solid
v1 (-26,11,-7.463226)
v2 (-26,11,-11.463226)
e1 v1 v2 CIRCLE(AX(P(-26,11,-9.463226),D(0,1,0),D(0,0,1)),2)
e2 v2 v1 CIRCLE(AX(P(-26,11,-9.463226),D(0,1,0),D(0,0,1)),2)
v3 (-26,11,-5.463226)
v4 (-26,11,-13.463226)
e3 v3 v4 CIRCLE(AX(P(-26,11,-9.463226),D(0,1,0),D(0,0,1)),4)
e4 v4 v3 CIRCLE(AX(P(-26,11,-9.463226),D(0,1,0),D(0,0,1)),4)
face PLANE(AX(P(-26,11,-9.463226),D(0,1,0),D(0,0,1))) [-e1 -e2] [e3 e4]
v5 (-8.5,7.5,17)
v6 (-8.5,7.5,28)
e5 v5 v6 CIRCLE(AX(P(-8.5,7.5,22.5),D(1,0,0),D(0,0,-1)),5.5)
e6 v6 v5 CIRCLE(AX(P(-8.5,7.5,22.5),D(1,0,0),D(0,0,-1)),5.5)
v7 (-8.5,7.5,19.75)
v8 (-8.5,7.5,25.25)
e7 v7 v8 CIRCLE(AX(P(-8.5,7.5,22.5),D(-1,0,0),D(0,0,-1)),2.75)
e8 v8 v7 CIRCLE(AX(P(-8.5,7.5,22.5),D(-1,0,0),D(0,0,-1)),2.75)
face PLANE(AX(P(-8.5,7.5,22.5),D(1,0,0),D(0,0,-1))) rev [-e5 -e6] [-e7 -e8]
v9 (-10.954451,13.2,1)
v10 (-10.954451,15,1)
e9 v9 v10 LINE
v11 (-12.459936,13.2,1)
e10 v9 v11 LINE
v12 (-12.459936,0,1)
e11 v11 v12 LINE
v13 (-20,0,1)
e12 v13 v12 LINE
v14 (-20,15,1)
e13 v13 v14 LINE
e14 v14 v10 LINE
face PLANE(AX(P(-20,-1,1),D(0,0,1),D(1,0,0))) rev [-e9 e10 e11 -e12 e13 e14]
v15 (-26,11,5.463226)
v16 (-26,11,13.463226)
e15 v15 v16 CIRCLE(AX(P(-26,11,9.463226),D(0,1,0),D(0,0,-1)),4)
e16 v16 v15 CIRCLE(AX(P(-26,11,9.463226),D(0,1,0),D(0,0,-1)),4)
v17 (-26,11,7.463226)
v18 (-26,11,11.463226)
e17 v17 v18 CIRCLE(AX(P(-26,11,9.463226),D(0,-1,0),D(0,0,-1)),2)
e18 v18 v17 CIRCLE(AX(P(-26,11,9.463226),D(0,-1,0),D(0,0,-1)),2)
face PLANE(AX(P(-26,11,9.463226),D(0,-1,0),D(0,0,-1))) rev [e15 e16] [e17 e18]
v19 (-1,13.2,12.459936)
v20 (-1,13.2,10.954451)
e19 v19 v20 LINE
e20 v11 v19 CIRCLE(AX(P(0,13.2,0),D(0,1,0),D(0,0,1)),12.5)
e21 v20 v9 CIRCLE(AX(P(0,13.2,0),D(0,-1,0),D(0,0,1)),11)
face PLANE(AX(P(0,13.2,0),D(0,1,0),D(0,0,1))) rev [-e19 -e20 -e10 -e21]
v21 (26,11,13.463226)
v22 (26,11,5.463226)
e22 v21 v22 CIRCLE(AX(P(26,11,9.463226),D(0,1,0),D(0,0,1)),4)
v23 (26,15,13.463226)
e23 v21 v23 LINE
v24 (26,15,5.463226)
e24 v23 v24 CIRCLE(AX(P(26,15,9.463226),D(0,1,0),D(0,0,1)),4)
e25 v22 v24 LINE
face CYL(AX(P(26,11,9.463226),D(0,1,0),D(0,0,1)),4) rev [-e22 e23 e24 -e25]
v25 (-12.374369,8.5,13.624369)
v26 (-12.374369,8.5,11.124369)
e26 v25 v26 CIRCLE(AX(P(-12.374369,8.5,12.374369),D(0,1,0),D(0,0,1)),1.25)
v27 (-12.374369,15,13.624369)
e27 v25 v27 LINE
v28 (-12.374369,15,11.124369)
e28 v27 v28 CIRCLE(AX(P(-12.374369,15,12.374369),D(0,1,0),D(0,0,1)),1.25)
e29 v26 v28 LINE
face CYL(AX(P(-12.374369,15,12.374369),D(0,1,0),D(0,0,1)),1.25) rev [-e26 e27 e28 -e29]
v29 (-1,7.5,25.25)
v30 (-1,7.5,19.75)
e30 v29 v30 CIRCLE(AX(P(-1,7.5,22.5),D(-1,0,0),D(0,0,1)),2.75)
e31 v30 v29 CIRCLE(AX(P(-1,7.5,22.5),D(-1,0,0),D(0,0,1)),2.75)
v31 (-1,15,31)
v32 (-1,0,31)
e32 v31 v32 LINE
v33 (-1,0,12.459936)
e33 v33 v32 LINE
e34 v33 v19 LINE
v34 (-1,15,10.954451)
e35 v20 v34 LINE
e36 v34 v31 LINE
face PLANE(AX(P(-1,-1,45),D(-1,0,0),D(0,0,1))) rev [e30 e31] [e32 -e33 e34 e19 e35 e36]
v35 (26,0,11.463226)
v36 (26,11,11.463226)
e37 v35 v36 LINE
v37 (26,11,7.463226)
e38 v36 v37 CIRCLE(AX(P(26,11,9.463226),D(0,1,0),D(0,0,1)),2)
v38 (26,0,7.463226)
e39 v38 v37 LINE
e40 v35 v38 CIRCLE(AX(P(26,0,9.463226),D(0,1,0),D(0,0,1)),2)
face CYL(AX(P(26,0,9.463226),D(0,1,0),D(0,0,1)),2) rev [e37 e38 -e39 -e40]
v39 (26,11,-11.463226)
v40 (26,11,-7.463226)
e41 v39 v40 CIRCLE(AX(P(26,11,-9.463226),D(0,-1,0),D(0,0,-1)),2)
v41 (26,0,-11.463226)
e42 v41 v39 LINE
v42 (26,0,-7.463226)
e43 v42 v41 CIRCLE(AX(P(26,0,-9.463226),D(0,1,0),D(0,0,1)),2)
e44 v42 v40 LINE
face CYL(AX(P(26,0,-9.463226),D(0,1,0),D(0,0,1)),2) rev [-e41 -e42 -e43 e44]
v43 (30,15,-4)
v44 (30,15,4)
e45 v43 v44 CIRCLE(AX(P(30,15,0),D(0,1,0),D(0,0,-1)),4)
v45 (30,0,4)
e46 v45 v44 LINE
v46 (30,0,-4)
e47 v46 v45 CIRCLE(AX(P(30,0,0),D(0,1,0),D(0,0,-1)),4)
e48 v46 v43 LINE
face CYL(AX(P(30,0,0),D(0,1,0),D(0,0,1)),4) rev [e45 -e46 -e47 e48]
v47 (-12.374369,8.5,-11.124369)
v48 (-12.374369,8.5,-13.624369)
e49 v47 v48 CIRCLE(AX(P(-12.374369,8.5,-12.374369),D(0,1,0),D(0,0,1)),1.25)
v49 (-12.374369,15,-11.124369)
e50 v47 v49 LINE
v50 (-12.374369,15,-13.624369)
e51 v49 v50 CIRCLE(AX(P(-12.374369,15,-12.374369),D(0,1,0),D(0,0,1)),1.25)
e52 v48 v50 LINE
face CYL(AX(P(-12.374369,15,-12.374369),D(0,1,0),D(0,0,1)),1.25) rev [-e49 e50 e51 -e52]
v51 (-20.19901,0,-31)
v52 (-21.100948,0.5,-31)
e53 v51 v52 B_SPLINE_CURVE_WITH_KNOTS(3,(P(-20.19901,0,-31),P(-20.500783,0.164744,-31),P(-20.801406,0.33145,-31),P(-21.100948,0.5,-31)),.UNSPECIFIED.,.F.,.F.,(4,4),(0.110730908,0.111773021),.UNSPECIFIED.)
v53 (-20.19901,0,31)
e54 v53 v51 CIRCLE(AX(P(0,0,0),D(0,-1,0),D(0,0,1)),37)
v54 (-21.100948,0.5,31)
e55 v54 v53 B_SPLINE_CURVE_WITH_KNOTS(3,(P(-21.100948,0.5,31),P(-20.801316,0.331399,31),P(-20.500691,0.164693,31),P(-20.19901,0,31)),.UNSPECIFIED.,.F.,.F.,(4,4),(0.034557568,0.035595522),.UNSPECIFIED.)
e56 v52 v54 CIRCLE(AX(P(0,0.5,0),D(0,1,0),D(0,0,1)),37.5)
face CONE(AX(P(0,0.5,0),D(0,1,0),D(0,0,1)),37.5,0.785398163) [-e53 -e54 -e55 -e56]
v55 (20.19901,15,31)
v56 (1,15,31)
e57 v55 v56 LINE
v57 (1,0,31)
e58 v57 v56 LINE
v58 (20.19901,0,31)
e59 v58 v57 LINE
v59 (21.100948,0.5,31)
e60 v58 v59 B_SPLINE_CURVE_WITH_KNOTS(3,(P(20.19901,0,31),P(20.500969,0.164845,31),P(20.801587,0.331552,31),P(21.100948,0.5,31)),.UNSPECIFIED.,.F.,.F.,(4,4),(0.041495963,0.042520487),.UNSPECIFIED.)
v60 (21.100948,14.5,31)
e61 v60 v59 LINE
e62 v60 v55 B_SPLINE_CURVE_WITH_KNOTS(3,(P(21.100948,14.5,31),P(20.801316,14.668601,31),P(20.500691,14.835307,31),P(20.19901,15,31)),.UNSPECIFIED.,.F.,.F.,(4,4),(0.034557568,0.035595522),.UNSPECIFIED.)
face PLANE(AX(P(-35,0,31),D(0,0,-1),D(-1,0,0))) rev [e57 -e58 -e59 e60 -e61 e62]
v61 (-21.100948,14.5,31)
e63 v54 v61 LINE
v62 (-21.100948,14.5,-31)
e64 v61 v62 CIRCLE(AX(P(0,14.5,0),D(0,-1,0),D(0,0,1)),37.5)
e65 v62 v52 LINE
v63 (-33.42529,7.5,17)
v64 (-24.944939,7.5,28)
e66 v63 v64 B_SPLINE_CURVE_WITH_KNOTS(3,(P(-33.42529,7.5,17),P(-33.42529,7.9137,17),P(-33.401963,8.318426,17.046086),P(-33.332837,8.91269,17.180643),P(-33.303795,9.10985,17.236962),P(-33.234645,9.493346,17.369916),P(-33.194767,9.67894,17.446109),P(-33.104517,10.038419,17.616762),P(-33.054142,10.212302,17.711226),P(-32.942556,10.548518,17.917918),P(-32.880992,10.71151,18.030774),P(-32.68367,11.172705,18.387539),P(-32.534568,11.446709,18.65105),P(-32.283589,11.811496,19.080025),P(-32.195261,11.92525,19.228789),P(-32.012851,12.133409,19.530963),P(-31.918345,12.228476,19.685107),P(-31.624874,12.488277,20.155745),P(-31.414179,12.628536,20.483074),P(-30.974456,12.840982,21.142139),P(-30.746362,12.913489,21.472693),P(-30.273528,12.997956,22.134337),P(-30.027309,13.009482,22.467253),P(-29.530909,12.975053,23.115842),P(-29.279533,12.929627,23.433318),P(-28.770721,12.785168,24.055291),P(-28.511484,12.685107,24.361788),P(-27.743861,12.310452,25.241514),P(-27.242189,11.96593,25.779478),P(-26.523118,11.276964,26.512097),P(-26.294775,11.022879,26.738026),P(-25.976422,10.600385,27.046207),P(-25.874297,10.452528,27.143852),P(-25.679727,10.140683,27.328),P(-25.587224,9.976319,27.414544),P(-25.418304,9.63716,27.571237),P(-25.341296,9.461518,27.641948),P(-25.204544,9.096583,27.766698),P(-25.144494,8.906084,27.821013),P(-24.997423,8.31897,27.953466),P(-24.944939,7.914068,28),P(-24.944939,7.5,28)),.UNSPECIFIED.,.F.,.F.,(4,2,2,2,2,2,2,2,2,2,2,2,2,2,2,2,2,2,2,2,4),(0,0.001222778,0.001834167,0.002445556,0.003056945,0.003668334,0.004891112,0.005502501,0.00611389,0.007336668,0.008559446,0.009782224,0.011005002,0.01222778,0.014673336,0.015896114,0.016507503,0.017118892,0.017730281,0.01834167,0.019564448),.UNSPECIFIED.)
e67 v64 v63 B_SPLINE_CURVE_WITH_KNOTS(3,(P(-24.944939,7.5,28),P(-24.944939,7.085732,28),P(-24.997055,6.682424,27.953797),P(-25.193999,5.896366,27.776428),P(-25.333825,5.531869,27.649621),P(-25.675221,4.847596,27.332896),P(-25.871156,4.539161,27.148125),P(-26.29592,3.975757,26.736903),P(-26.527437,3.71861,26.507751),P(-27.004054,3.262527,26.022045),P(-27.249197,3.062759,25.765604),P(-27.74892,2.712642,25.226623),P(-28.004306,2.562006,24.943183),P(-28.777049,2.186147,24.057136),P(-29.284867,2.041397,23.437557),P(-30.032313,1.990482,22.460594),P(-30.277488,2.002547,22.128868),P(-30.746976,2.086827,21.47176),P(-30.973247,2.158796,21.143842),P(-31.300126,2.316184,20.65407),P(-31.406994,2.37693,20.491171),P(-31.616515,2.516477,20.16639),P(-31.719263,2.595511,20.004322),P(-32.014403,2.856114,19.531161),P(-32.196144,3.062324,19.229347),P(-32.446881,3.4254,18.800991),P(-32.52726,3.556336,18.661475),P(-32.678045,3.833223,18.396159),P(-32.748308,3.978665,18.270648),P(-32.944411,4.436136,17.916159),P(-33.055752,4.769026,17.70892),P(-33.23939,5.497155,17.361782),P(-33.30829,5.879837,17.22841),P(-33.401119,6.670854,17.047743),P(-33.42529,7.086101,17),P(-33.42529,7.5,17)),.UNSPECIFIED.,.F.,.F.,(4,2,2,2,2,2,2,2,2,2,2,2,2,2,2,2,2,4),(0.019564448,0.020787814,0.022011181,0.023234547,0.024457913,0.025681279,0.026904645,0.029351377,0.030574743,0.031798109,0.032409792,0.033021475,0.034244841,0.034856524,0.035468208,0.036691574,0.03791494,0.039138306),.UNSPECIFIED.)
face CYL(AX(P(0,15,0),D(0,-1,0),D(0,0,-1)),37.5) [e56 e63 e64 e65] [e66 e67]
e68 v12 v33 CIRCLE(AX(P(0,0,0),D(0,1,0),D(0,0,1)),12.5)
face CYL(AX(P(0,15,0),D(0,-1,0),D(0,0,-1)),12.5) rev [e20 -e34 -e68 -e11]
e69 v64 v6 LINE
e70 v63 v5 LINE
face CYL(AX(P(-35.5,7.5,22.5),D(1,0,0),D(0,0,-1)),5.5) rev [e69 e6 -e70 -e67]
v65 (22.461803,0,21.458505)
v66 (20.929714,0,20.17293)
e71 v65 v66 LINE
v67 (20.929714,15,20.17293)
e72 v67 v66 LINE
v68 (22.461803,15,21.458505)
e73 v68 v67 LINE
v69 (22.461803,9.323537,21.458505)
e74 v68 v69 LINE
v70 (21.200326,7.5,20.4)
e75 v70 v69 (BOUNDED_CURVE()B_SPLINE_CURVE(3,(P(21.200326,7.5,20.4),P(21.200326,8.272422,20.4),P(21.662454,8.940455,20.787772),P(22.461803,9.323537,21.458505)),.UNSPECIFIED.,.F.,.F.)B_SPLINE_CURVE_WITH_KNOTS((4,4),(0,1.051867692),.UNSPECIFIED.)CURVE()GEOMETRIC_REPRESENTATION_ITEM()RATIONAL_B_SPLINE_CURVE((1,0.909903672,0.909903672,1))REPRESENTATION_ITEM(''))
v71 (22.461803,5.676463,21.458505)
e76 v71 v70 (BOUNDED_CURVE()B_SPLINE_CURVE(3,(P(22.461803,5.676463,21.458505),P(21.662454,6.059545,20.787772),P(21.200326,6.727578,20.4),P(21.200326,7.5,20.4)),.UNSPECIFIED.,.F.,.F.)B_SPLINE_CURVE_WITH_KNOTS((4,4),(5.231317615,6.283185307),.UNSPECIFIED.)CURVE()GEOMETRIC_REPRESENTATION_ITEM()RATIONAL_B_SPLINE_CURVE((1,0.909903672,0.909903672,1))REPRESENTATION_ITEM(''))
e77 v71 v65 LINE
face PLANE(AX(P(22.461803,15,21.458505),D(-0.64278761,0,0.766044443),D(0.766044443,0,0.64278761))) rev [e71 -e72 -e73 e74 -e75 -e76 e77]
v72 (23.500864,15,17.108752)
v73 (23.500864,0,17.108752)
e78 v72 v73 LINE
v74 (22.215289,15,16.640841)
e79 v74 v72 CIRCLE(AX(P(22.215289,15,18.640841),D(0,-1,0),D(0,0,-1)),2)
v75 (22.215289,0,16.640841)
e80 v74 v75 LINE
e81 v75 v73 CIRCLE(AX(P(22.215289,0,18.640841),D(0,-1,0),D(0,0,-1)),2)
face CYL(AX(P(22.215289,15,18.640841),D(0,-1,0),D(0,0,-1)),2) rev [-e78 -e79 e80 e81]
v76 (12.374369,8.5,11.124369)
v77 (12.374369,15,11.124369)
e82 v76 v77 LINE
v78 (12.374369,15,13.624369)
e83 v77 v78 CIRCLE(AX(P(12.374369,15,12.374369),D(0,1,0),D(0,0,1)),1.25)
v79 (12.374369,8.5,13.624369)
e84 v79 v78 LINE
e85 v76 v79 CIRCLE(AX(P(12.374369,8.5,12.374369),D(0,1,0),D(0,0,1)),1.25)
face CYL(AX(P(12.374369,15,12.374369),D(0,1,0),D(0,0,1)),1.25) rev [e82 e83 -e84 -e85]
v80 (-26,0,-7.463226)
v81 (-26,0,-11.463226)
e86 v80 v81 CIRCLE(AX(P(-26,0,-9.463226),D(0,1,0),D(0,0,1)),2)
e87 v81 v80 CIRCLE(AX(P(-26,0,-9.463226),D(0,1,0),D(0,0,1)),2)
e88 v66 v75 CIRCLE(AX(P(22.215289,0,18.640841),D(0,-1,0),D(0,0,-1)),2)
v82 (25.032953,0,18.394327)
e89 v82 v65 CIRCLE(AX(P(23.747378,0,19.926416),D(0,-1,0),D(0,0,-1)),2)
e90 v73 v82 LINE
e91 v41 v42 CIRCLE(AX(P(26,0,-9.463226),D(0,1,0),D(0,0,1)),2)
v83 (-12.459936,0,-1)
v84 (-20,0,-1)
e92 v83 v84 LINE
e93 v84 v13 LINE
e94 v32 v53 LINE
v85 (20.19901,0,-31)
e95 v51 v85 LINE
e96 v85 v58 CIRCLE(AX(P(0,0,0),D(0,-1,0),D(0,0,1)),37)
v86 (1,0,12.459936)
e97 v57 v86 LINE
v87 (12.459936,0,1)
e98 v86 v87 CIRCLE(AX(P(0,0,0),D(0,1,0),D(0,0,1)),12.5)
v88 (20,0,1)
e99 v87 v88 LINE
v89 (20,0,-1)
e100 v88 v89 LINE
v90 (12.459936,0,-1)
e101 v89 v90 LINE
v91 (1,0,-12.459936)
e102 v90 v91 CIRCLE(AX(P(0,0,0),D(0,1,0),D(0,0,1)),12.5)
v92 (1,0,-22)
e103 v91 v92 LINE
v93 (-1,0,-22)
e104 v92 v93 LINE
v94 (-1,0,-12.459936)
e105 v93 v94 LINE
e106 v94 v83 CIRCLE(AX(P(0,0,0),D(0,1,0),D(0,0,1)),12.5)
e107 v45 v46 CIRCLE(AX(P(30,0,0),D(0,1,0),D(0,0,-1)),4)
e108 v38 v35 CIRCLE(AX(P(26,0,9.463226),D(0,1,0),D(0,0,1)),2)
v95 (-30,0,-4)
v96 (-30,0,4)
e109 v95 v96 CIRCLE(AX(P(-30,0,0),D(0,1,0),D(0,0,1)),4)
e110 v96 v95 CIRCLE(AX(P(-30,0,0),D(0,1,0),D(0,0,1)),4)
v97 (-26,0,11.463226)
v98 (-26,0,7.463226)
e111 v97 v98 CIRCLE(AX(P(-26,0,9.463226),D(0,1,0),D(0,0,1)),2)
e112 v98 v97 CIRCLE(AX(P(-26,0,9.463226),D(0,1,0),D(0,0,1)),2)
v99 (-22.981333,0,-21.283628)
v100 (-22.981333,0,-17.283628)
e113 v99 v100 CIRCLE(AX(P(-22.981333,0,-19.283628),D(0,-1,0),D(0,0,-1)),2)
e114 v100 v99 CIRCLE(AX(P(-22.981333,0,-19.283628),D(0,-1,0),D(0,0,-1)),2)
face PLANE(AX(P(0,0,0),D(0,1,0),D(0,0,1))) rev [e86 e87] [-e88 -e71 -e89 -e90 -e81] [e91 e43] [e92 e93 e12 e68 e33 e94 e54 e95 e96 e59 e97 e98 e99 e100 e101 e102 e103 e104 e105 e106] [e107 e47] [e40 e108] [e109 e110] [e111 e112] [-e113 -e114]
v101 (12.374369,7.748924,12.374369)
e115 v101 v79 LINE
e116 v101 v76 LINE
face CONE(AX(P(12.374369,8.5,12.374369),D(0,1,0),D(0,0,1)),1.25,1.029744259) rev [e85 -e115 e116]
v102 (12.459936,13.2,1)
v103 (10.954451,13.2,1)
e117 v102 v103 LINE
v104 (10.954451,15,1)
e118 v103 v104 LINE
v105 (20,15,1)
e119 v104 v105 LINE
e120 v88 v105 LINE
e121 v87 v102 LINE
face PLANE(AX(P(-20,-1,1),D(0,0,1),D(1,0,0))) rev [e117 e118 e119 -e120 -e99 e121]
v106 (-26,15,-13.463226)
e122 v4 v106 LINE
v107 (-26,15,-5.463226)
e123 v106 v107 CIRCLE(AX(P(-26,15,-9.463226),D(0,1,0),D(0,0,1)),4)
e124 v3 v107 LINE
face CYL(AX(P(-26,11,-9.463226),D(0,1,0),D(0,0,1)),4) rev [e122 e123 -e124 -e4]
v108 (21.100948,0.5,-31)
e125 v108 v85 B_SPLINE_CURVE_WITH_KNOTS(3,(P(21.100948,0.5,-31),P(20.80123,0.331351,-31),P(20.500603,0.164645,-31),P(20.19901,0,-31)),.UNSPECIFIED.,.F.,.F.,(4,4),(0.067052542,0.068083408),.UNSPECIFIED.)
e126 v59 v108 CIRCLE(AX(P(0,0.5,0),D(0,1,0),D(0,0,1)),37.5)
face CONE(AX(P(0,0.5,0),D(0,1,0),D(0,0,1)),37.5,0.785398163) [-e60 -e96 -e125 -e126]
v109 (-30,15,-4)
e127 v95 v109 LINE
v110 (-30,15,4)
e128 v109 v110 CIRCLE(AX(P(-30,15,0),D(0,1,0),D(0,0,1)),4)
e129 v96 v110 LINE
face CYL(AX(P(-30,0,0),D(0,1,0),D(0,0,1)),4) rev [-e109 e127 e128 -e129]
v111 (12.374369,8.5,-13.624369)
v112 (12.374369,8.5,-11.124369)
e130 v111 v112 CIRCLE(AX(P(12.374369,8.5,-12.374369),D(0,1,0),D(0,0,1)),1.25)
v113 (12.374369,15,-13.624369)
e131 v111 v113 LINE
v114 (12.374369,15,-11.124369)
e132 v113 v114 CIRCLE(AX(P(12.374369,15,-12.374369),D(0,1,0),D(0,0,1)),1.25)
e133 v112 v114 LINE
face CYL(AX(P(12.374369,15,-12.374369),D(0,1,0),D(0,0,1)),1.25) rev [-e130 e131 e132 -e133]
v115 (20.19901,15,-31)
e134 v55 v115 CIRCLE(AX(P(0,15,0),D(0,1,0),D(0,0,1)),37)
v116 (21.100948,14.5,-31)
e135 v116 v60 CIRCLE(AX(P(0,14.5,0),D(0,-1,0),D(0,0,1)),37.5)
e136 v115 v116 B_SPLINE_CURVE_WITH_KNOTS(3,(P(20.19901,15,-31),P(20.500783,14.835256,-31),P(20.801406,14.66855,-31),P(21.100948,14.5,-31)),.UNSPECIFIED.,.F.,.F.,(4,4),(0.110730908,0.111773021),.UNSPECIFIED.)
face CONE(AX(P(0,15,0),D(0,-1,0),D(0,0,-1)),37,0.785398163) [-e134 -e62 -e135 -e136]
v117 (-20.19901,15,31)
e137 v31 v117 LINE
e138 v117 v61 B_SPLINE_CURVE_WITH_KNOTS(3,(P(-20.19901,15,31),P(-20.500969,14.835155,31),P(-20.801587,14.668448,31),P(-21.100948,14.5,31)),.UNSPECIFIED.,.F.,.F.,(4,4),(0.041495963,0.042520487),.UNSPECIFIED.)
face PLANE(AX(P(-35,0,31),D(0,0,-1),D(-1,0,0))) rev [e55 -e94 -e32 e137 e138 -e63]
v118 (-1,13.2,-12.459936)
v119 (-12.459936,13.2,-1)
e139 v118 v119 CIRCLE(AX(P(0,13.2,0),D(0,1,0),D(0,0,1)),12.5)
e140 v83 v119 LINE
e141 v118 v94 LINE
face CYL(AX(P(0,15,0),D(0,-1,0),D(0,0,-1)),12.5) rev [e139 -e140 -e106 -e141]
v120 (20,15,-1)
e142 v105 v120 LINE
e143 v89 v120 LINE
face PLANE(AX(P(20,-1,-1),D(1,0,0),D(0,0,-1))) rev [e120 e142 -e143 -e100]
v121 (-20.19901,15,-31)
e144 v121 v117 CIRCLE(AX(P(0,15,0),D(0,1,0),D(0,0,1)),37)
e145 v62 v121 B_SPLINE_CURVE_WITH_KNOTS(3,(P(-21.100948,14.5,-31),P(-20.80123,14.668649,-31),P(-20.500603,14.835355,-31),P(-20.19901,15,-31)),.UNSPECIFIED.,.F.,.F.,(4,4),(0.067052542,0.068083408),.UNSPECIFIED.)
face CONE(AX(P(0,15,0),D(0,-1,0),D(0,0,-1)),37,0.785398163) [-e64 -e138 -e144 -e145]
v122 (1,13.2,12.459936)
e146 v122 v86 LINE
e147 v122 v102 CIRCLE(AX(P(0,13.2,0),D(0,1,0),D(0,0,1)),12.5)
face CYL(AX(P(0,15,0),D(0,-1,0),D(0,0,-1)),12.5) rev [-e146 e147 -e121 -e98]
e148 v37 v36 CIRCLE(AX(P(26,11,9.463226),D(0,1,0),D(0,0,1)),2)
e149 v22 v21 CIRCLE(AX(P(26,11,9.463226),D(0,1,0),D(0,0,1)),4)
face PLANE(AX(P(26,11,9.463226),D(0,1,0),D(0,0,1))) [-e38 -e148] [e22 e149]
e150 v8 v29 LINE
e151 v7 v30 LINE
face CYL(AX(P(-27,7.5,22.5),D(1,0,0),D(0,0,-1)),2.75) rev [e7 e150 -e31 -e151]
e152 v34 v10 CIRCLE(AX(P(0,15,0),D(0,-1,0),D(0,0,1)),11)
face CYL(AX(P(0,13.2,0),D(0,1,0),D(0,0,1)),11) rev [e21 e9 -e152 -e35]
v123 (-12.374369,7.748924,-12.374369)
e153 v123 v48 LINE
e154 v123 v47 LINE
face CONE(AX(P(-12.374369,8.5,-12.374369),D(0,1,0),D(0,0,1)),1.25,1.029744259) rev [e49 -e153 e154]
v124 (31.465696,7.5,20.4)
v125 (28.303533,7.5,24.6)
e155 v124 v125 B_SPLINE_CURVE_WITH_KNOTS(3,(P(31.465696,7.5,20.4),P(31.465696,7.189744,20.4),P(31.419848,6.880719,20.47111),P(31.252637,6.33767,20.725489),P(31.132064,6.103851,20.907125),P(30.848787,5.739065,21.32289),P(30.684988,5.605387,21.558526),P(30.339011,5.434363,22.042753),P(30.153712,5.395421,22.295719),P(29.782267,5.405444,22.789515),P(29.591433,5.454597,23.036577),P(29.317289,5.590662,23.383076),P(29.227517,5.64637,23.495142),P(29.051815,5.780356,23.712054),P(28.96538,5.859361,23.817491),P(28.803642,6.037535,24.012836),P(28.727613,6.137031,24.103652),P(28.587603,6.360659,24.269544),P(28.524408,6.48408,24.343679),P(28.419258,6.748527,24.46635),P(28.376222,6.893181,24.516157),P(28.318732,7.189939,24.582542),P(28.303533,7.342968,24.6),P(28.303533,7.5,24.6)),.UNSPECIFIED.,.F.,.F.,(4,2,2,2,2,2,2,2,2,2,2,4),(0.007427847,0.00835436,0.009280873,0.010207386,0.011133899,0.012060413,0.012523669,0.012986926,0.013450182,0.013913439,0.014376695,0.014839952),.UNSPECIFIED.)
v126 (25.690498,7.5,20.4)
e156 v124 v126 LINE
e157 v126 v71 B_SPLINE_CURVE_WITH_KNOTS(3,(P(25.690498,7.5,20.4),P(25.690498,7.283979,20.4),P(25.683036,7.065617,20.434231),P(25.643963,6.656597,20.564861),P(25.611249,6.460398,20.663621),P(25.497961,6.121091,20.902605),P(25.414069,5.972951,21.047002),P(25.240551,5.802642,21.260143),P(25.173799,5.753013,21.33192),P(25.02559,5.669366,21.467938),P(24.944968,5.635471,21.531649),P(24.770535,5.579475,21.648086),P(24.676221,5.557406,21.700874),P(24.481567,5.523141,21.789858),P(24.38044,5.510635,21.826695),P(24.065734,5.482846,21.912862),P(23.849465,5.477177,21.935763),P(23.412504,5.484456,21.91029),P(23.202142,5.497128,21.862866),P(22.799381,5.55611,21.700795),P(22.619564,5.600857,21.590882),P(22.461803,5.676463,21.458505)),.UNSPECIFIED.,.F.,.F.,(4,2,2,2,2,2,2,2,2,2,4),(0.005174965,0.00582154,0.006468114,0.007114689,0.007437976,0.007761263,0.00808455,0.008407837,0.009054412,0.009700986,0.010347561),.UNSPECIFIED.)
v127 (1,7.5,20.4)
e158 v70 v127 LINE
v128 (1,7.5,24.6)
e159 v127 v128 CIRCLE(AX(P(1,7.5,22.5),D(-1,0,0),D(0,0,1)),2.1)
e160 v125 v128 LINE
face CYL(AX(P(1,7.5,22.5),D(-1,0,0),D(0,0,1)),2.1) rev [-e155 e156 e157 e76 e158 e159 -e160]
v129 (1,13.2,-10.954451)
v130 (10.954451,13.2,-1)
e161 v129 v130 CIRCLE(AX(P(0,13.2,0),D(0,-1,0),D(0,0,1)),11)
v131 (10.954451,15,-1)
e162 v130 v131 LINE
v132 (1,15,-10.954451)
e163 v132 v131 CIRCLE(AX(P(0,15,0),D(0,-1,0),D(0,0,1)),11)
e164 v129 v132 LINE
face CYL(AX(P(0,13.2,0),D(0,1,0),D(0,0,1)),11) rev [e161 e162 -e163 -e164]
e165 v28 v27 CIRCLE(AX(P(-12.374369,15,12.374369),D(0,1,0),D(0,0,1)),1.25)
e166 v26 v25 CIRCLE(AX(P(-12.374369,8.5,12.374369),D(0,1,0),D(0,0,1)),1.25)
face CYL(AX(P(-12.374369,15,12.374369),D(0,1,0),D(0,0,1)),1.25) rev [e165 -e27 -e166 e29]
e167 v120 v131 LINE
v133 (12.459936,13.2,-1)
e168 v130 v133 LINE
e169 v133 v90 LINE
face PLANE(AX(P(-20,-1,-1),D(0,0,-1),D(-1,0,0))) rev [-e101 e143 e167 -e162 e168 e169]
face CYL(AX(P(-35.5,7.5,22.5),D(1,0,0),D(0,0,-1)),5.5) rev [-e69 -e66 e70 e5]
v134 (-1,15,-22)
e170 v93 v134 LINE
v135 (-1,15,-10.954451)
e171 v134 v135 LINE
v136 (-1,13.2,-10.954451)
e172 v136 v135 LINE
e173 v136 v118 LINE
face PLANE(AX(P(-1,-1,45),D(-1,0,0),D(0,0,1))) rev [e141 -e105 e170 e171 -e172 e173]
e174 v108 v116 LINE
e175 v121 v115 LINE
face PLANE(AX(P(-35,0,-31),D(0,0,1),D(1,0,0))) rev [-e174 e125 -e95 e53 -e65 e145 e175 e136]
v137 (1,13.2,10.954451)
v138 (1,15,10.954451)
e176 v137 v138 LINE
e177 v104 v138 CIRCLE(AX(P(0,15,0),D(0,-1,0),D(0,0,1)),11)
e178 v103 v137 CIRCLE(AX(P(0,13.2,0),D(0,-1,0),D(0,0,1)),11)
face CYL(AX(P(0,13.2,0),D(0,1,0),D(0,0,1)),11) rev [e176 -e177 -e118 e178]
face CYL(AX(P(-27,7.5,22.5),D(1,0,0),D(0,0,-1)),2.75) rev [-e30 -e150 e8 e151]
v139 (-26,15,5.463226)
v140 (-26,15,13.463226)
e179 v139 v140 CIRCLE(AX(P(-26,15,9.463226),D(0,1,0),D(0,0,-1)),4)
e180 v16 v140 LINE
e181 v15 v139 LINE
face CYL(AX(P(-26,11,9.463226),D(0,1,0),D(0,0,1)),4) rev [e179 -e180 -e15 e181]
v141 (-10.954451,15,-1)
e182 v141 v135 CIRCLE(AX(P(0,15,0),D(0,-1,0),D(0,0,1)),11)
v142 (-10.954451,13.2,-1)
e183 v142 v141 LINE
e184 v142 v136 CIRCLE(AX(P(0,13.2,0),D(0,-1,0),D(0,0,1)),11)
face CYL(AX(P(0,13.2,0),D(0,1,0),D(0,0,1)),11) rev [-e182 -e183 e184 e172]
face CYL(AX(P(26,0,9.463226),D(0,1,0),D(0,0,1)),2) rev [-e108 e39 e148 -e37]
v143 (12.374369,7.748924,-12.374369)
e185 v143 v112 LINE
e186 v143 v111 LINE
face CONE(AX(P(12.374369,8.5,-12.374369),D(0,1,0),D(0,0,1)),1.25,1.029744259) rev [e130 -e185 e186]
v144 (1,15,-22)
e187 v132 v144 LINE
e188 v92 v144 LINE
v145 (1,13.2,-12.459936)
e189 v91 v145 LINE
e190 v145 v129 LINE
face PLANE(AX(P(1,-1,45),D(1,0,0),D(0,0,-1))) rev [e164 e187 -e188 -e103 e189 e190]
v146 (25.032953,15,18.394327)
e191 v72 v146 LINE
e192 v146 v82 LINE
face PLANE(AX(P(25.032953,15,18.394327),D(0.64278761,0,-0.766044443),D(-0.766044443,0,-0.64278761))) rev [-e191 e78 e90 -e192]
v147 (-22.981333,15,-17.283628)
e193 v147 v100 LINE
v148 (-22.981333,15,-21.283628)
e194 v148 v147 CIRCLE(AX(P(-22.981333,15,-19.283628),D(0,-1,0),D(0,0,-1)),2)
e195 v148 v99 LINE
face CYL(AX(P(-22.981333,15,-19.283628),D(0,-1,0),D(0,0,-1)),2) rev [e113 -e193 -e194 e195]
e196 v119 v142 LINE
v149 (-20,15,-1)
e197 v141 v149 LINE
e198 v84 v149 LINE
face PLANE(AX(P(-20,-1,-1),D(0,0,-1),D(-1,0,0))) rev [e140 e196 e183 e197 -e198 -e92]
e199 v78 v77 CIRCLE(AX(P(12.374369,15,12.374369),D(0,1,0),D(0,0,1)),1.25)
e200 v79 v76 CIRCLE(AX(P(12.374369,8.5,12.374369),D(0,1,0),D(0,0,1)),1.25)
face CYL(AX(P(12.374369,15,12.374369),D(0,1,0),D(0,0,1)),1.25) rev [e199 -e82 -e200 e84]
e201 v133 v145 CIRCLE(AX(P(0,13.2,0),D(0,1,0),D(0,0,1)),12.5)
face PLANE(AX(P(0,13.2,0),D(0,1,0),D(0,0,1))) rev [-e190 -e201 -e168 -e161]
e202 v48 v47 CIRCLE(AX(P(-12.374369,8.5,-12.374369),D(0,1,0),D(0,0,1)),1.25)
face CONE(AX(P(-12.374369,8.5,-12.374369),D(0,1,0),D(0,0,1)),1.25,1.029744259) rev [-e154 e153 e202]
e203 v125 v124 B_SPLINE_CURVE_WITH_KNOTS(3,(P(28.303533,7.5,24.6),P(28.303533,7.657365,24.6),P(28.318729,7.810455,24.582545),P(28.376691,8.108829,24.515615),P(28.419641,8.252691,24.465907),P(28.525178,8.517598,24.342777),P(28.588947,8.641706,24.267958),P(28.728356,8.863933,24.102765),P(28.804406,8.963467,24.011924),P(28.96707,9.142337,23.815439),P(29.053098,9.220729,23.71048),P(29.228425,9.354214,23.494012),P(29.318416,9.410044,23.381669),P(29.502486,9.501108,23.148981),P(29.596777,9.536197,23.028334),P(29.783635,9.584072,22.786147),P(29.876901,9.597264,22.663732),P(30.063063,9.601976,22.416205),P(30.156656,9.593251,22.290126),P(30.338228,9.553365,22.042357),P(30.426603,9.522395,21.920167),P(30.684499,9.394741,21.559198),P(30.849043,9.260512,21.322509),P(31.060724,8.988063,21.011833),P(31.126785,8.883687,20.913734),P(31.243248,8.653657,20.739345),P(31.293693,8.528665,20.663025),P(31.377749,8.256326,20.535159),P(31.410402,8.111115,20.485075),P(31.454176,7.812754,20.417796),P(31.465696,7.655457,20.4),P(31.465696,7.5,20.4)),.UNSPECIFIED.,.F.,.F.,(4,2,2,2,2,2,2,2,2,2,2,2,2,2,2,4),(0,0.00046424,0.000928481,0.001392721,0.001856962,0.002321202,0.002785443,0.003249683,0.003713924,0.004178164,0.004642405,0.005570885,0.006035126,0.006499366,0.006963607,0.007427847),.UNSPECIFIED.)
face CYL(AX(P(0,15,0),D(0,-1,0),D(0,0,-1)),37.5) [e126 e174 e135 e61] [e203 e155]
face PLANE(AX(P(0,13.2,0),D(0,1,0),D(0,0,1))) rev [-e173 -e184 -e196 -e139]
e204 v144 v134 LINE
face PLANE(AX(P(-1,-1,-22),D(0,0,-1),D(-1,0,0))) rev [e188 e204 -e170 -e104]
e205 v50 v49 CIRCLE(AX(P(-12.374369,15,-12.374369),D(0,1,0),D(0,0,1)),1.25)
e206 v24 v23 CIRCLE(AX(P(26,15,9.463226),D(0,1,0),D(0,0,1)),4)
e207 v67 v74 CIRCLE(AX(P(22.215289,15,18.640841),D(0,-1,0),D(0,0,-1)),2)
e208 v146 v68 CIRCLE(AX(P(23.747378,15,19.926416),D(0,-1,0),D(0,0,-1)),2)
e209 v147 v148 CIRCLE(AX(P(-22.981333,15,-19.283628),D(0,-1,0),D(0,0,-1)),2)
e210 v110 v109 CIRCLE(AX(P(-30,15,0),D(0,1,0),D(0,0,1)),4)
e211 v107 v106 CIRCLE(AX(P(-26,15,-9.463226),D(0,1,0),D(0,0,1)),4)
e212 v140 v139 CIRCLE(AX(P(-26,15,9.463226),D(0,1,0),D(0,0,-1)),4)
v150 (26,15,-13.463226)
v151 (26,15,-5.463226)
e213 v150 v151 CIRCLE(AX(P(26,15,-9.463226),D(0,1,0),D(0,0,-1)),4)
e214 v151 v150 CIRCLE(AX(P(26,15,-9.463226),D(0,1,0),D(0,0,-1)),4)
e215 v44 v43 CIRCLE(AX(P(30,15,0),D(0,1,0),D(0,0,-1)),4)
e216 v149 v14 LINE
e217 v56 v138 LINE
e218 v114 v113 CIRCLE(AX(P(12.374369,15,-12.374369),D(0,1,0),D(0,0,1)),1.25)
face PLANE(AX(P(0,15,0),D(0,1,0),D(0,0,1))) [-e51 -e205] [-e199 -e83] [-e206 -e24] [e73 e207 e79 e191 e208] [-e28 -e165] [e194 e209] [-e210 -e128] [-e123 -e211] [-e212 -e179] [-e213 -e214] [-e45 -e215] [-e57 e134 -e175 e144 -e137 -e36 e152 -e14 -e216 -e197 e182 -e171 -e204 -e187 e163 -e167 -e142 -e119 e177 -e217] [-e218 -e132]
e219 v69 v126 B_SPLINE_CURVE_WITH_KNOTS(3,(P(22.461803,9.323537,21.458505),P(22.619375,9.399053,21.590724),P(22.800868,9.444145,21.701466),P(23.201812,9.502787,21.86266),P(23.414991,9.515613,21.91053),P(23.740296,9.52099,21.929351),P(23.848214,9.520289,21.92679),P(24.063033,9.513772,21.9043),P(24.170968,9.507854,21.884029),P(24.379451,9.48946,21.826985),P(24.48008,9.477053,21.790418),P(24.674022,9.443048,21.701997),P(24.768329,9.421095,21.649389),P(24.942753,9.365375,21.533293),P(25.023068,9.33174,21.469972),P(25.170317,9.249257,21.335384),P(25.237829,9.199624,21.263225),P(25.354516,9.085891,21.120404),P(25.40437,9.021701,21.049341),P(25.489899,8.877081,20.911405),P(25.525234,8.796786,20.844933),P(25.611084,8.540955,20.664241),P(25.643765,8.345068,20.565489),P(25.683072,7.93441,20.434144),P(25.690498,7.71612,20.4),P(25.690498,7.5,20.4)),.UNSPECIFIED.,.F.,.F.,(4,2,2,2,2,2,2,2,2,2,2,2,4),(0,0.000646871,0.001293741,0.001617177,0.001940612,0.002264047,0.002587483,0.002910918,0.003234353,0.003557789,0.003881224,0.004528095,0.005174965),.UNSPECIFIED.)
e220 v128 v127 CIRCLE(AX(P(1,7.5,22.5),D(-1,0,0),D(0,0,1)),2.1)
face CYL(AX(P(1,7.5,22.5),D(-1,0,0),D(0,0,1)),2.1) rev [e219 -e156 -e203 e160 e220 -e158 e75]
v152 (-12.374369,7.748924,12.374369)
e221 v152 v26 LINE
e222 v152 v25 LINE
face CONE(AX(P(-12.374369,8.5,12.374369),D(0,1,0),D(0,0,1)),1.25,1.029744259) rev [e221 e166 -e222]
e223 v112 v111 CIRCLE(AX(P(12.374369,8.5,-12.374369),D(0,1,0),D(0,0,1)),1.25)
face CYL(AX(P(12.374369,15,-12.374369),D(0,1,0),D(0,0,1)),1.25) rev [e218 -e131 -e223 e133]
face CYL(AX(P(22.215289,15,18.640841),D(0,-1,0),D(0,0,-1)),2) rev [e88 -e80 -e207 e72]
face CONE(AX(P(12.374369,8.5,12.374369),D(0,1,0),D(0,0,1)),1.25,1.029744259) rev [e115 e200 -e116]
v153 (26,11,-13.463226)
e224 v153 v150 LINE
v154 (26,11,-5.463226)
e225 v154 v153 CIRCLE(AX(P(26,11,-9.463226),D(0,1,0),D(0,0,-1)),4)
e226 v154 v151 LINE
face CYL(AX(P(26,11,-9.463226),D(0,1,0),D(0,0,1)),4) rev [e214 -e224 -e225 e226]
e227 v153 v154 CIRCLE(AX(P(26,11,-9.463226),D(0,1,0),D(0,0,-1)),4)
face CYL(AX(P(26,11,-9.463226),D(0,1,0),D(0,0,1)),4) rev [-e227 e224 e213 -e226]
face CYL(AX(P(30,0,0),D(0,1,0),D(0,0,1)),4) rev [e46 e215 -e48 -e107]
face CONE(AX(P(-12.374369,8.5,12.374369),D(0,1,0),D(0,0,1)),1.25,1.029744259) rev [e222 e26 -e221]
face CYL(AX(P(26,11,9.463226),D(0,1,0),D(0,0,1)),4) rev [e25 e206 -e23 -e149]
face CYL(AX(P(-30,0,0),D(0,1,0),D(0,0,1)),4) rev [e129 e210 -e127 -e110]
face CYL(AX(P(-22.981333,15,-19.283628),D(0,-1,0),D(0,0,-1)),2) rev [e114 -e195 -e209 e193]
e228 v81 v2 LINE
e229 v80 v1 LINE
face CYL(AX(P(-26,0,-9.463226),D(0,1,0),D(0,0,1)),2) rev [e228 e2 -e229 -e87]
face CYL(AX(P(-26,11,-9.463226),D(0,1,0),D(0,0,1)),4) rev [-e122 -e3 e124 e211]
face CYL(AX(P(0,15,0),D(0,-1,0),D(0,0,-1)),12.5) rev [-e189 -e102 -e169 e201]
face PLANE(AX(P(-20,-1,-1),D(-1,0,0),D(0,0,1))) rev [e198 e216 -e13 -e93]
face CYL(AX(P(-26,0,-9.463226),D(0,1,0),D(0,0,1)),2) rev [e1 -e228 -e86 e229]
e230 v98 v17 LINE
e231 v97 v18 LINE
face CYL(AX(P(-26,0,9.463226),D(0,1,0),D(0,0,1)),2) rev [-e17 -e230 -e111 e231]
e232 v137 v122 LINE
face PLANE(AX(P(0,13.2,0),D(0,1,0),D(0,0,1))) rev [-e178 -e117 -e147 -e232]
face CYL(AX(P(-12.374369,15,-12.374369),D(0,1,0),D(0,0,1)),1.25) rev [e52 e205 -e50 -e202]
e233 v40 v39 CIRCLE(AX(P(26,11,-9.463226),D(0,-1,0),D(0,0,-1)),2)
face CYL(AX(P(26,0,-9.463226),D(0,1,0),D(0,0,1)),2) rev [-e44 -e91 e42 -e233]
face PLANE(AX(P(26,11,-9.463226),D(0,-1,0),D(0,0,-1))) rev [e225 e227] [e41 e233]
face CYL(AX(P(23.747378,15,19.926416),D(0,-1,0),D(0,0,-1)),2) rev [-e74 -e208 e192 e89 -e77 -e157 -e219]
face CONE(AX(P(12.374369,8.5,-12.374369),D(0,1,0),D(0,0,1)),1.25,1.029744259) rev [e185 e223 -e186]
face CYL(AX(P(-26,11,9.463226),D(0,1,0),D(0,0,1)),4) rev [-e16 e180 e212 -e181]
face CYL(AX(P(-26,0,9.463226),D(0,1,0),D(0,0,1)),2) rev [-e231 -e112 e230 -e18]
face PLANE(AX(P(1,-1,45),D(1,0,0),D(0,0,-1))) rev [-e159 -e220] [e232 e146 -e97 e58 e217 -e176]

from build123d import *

# Parameters (mm, degrees)
SKETCH1_R           = 37.5
SKETCH1_R_2         = 12.5
BOSS_EXTRUDE1_DEPTH = 15
SKETCH2_R           = 4
CUT_EXTRUDE1_DEPTH  = 4
SKETCH3_R           = 2
CUT_EXTRUDE2_DEPTH  = 56.113519213
SKETCH4_W           = 40
SKETCH4_H           = 2
CUT_EXTRUDE3_DEPTH  = 16
SKETCH5_W           = 2
SKETCH5_H           = 67
CUT_EXTRUDE4_DEPTH  = 16
CHAMFER1_SIZE       = 0.5
SKETCH6_R           = 2.75
CUT_EXTRUDE5_DEPTH  = 27
SKETCH7_R           = 5.5
CUT_EXTRUDE6_DEPTH  = 27
SKETCH8_R           = 0.542778956
CUT_EXTRUDE7_DEPTH  = 27
M5_TAPPED_HOLE1_D   = 4.2
SKETCH10_R          = 4
CUT_EXTRUDE8_DEPTH  = 56.113519349
SKETCH11_W          = 70
SKETCH11_H          = 13
CUT_EXTRUDE9_DEPTH  = 56.113519349
SKETCH16_R          = 2
CUT_EXTRUDE11_DEPTH = 51.914143553
BOSS_EXTRUDE2_START = -1.8
BOSS_EXTRUDE2_DEPTH = 1.8
SKETCH19_R          = 1
CUT_EXTRUDE12_DEPTH = 5
CIRPATTERN2_COUNT   = 4


with BuildPart() as part:
    # Sketch1 → Boss-Extrude1 (new body)
    with BuildSketch(Plane(origin=(0, 0, 0), x_dir=(1, 0, 0), z_dir=(0, 1, 0))):
        with Locations(Location((0, 0, 0), (0, 0, 270))):
            Circle(SKETCH1_R)
        with Locations(Location((0, 0, 0), (0, 0, 270))):
            Circle(SKETCH1_R_2, mode=Mode.SUBTRACT)
    extrude(amount=BOSS_EXTRUDE1_DEPTH)

    # Sketch2 → Cut-Extrude1 (cut)
    with BuildSketch(Plane(origin=(0, 15, 0), x_dir=(1, 0, 0), z_dir=(0, 1, 0))):
        with Locations(Location((26, -9.463226091, 0), (0, 0, 270))):
            Circle(SKETCH2_R)
        with Locations(Location((-26, 9.463226091, 0), (0, 0, 270))):
            Circle(SKETCH2_R)
        with Locations(Location((-26, -9.463226091, 0), (0, 0, 90))):
            Circle(SKETCH2_R)
        with Locations(Location((26, 9.463226091, 0), (0, 0, 90))):
            Circle(SKETCH2_R)
    extrude(amount=-CUT_EXTRUDE1_DEPTH, mode=Mode.SUBTRACT)

    # Sketch3 → Cut-Extrude2 (cut, through all)
    with BuildSketch(Plane(origin=(0, 15, 0), x_dir=(1, 0, 0), z_dir=(0, 1, 0))):
        with Locations(Location((-26, 9.463226091, 0), (0, 0, 270))):
            Circle(SKETCH3_R)
        with Locations(Location((-26, -9.463226091, 0), (0, 0, 270))):
            Circle(SKETCH3_R)
        with Locations(Location((26, 9.463226091, 0), (0, 0, 270))):
            Circle(SKETCH3_R)
        with Locations(Location((26, -9.463226091, 0), (0, 0, 270))):
            Circle(SKETCH3_R)
    extrude(amount=-CUT_EXTRUDE2_DEPTH, mode=Mode.SUBTRACT)

    # Sketch4 → Cut-Extrude3 (cut)
    with BuildSketch(Plane(origin=(0, 15, 0), x_dir=(1, 0, 0), z_dir=(0, 1, 0))):
        Rectangle(SKETCH4_W, SKETCH4_H)
    extrude(amount=-CUT_EXTRUDE3_DEPTH, mode=Mode.SUBTRACT)

    # Sketch5 → Cut-Extrude4 (cut)
    with BuildSketch(Plane(origin=(0, 15, 0), x_dir=(1, 0, 0), z_dir=(0, 1, 0))):
        with Locations((0, -11.5)):
            Rectangle(SKETCH5_W, SKETCH5_H)
    extrude(amount=-CUT_EXTRUDE4_DEPTH, mode=Mode.SUBTRACT)

    # Chamfer1
    chamfer1_edges = [part.edges().sort_by_distance(p)[0] for p in [
        (0, 0, -37.5),
        (0, 15, -37.5),
    ]]
    chamfer(chamfer1_edges, length=CHAMFER1_SIZE)

    # Sketch6 → Cut-Extrude5 (cut)
    with BuildSketch(Plane(origin=(0, 0, 0), x_dir=(0, 0, -1), z_dir=(1, 0, 0))):
        with Locations((-22.5, 7.5)):
            Circle(SKETCH6_R)
    extrude(amount=-CUT_EXTRUDE5_DEPTH, mode=Mode.SUBTRACT)

    # Sketch7 → Cut-Extrude6 (cut)
    with BuildSketch(Plane(origin=(-8.5, 0, 0), x_dir=(0, 0, -1), z_dir=(1, 0, 0))):
        with Locations((-22.5, 7.5)):
            Circle(SKETCH7_R)
    extrude(amount=-CUT_EXTRUDE6_DEPTH, mode=Mode.SUBTRACT)

    # Sketch8 → Cut-Extrude7 (cut)
    with BuildSketch(Plane.ZY.offset(-1)):
        with Locations((22.5, 7.5)):
            Circle(SKETCH8_R)
    extrude(amount=-CUT_EXTRUDE7_DEPTH, mode=Mode.SUBTRACT)

    # M5 Tapped Hole1 (through all)
    with Locations(Plane(origin=(1, 7.5, 22.5), x_dir=(0, 0, -1), z_dir=(-1, 0, 0))):
        with Locations((0, 0)):
            Hole(M5_TAPPED_HOLE1_D / 2)

    # Sketch10 → Cut-Extrude8 (cut, through all)
    with BuildSketch(Plane(origin=(0, 15, 0), x_dir=(1, 0, 0), z_dir=(0, 1, 0))):
        with Locations(Location((-30, 0, 0), (0, 0, 270))):
            Circle(SKETCH10_R)
        with Locations(Location((30, 0, 0), (0, 0, 90))):
            Circle(SKETCH10_R)
    extrude(amount=-CUT_EXTRUDE8_DEPTH, mode=Mode.SUBTRACT)

    # Sketch11 → Cut-Extrude9 (cut, through all)
    with BuildSketch(Plane(origin=(0, 15, 0), x_dir=(1, 0, 0), z_dir=(0, 1, 0))):
        with Locations((0, -37.5)):
            Rectangle(SKETCH11_W, SKETCH11_H)
        with Locations((0, 37.5)):
            Rectangle(SKETCH11_W, SKETCH11_H)
    extrude(amount=-CUT_EXTRUDE9_DEPTH, mode=Mode.SUBTRACT)

    # Sketch16 → Cut-Extrude11 (cut, through all)
    with BuildSketch(Plane.XZ):
        with Locations(Location((-22.981333294, -19.283628291, 0), (0, 0, 270))):
            Circle(SKETCH16_R)
        with BuildLine():
            Line((25.032952956, 18.394327014), (23.50086407, 17.108751795))
            ThreePointArc((23.50086407, 17.108751795), (20.683199964, 17.355265462), (20.929713631, 20.172929567))
            Line((20.929713631, 20.172929567), (22.461802517, 21.458504787))
            ThreePointArc((22.461802517, 21.458504787), (25.279466623, 21.21199112), (25.032952956, 18.394327014))
        make_face()
    extrude(amount=-CUT_EXTRUDE11_DEPTH, mode=Mode.SUBTRACT)

    # Sketch17 → Boss-Extrude2 (add)
    with BuildSketch(Plane(origin=(0, 15, 0), x_dir=(1, 0, 0), z_dir=(0, 1, 0)).offset(BOSS_EXTRUDE2_START)):
        with BuildLine():
            Line((1, 12.459935794), (1, 10.95445115))
            ThreePointArc((1, 10.95445115), (7.778174593, 7.778174593), (10.95445115, 1))
            Line((10.95445115, 1), (12.459935794, 1))
            ThreePointArc((12.459935794, 1), (8.838834765, 8.838834765), (1, 12.459935794))
        make_face()
        with BuildLine():
            Line((-1, 12.459935794), (-1, 10.95445115))
            ThreePointArc((-1, 10.95445115), (-7.778174593, 7.778174593), (-10.95445115, 1))
            Line((-10.95445115, 1), (-12.459935794, 1))
            ThreePointArc((-12.459935794, 1), (-8.838834765, 8.838834765), (-1, 12.459935794))
        make_face()
        with BuildLine():
            Line((12.459935794, -1), (10.95445115, -1))
            ThreePointArc((10.95445115, -1), (7.778174593, -7.778174593), (1, -10.95445115))
            Line((1, -10.95445115), (1, -12.459935794))
            ThreePointArc((1, -12.459935794), (8.838834765, -8.838834765), (12.459935794, -1))
        make_face()
        with BuildLine():
            Line((-12.459935794, -1), (-10.95445115, -1))
            ThreePointArc((-10.95445115, -1), (-7.778174593, -7.778174593), (-1, -10.95445115))
            Line((-1, -10.95445115), (-1, -12.459935794))
            ThreePointArc((-1, -12.459935794), (-8.838834765, -8.838834765), (-12.459935794, -1))
        make_face()
    extrude(amount=BOSS_EXTRUDE2_DEPTH)

    # Sketch19 → Cut-Extrude12 (cut)
    with BuildSketch(Plane(origin=(0, 15, 0), x_dir=(1, 0, 0), z_dir=(0, 1, 0))):
        with Locations(Location((-12.374368671, 12.374368671, 0), (0, 0, 270))):
            Circle(SKETCH19_R)
    extrude(amount=-CUT_EXTRUDE12_DEPTH, mode=Mode.SUBTRACT)

    # Sketch20 → M3 Tapped Hole2 (revolve, cut)
    with BuildSketch(Plane(origin=(-12.374368671, 15, -12.374368671), x_dir=(0, 0, 1), z_dir=(1, 0, 0))):
        Polygon((0, 0), (0, 7.251075774), (1.25, 6.5), (1.25, 0), align=None)
    m3_tapped_hole2 = revolve(axis=Axis((-12.374368671, 21.35, -12.374368671), (0, -1, 0)), mode=Mode.SUBTRACT)

    # CirPattern2: M3 Tapped Hole2 ×4 about axis
    cirpattern2_axis = Axis((0, 0, 0), (0, 1, 0))
    for i in range(1, CIRPATTERN2_COUNT):
        add(m3_tapped_hole2.rotate(cirpattern2_axis, i * 360 / CIRPATTERN2_COUNT), mode=Mode.SUBTRACT)


solid = part.part
